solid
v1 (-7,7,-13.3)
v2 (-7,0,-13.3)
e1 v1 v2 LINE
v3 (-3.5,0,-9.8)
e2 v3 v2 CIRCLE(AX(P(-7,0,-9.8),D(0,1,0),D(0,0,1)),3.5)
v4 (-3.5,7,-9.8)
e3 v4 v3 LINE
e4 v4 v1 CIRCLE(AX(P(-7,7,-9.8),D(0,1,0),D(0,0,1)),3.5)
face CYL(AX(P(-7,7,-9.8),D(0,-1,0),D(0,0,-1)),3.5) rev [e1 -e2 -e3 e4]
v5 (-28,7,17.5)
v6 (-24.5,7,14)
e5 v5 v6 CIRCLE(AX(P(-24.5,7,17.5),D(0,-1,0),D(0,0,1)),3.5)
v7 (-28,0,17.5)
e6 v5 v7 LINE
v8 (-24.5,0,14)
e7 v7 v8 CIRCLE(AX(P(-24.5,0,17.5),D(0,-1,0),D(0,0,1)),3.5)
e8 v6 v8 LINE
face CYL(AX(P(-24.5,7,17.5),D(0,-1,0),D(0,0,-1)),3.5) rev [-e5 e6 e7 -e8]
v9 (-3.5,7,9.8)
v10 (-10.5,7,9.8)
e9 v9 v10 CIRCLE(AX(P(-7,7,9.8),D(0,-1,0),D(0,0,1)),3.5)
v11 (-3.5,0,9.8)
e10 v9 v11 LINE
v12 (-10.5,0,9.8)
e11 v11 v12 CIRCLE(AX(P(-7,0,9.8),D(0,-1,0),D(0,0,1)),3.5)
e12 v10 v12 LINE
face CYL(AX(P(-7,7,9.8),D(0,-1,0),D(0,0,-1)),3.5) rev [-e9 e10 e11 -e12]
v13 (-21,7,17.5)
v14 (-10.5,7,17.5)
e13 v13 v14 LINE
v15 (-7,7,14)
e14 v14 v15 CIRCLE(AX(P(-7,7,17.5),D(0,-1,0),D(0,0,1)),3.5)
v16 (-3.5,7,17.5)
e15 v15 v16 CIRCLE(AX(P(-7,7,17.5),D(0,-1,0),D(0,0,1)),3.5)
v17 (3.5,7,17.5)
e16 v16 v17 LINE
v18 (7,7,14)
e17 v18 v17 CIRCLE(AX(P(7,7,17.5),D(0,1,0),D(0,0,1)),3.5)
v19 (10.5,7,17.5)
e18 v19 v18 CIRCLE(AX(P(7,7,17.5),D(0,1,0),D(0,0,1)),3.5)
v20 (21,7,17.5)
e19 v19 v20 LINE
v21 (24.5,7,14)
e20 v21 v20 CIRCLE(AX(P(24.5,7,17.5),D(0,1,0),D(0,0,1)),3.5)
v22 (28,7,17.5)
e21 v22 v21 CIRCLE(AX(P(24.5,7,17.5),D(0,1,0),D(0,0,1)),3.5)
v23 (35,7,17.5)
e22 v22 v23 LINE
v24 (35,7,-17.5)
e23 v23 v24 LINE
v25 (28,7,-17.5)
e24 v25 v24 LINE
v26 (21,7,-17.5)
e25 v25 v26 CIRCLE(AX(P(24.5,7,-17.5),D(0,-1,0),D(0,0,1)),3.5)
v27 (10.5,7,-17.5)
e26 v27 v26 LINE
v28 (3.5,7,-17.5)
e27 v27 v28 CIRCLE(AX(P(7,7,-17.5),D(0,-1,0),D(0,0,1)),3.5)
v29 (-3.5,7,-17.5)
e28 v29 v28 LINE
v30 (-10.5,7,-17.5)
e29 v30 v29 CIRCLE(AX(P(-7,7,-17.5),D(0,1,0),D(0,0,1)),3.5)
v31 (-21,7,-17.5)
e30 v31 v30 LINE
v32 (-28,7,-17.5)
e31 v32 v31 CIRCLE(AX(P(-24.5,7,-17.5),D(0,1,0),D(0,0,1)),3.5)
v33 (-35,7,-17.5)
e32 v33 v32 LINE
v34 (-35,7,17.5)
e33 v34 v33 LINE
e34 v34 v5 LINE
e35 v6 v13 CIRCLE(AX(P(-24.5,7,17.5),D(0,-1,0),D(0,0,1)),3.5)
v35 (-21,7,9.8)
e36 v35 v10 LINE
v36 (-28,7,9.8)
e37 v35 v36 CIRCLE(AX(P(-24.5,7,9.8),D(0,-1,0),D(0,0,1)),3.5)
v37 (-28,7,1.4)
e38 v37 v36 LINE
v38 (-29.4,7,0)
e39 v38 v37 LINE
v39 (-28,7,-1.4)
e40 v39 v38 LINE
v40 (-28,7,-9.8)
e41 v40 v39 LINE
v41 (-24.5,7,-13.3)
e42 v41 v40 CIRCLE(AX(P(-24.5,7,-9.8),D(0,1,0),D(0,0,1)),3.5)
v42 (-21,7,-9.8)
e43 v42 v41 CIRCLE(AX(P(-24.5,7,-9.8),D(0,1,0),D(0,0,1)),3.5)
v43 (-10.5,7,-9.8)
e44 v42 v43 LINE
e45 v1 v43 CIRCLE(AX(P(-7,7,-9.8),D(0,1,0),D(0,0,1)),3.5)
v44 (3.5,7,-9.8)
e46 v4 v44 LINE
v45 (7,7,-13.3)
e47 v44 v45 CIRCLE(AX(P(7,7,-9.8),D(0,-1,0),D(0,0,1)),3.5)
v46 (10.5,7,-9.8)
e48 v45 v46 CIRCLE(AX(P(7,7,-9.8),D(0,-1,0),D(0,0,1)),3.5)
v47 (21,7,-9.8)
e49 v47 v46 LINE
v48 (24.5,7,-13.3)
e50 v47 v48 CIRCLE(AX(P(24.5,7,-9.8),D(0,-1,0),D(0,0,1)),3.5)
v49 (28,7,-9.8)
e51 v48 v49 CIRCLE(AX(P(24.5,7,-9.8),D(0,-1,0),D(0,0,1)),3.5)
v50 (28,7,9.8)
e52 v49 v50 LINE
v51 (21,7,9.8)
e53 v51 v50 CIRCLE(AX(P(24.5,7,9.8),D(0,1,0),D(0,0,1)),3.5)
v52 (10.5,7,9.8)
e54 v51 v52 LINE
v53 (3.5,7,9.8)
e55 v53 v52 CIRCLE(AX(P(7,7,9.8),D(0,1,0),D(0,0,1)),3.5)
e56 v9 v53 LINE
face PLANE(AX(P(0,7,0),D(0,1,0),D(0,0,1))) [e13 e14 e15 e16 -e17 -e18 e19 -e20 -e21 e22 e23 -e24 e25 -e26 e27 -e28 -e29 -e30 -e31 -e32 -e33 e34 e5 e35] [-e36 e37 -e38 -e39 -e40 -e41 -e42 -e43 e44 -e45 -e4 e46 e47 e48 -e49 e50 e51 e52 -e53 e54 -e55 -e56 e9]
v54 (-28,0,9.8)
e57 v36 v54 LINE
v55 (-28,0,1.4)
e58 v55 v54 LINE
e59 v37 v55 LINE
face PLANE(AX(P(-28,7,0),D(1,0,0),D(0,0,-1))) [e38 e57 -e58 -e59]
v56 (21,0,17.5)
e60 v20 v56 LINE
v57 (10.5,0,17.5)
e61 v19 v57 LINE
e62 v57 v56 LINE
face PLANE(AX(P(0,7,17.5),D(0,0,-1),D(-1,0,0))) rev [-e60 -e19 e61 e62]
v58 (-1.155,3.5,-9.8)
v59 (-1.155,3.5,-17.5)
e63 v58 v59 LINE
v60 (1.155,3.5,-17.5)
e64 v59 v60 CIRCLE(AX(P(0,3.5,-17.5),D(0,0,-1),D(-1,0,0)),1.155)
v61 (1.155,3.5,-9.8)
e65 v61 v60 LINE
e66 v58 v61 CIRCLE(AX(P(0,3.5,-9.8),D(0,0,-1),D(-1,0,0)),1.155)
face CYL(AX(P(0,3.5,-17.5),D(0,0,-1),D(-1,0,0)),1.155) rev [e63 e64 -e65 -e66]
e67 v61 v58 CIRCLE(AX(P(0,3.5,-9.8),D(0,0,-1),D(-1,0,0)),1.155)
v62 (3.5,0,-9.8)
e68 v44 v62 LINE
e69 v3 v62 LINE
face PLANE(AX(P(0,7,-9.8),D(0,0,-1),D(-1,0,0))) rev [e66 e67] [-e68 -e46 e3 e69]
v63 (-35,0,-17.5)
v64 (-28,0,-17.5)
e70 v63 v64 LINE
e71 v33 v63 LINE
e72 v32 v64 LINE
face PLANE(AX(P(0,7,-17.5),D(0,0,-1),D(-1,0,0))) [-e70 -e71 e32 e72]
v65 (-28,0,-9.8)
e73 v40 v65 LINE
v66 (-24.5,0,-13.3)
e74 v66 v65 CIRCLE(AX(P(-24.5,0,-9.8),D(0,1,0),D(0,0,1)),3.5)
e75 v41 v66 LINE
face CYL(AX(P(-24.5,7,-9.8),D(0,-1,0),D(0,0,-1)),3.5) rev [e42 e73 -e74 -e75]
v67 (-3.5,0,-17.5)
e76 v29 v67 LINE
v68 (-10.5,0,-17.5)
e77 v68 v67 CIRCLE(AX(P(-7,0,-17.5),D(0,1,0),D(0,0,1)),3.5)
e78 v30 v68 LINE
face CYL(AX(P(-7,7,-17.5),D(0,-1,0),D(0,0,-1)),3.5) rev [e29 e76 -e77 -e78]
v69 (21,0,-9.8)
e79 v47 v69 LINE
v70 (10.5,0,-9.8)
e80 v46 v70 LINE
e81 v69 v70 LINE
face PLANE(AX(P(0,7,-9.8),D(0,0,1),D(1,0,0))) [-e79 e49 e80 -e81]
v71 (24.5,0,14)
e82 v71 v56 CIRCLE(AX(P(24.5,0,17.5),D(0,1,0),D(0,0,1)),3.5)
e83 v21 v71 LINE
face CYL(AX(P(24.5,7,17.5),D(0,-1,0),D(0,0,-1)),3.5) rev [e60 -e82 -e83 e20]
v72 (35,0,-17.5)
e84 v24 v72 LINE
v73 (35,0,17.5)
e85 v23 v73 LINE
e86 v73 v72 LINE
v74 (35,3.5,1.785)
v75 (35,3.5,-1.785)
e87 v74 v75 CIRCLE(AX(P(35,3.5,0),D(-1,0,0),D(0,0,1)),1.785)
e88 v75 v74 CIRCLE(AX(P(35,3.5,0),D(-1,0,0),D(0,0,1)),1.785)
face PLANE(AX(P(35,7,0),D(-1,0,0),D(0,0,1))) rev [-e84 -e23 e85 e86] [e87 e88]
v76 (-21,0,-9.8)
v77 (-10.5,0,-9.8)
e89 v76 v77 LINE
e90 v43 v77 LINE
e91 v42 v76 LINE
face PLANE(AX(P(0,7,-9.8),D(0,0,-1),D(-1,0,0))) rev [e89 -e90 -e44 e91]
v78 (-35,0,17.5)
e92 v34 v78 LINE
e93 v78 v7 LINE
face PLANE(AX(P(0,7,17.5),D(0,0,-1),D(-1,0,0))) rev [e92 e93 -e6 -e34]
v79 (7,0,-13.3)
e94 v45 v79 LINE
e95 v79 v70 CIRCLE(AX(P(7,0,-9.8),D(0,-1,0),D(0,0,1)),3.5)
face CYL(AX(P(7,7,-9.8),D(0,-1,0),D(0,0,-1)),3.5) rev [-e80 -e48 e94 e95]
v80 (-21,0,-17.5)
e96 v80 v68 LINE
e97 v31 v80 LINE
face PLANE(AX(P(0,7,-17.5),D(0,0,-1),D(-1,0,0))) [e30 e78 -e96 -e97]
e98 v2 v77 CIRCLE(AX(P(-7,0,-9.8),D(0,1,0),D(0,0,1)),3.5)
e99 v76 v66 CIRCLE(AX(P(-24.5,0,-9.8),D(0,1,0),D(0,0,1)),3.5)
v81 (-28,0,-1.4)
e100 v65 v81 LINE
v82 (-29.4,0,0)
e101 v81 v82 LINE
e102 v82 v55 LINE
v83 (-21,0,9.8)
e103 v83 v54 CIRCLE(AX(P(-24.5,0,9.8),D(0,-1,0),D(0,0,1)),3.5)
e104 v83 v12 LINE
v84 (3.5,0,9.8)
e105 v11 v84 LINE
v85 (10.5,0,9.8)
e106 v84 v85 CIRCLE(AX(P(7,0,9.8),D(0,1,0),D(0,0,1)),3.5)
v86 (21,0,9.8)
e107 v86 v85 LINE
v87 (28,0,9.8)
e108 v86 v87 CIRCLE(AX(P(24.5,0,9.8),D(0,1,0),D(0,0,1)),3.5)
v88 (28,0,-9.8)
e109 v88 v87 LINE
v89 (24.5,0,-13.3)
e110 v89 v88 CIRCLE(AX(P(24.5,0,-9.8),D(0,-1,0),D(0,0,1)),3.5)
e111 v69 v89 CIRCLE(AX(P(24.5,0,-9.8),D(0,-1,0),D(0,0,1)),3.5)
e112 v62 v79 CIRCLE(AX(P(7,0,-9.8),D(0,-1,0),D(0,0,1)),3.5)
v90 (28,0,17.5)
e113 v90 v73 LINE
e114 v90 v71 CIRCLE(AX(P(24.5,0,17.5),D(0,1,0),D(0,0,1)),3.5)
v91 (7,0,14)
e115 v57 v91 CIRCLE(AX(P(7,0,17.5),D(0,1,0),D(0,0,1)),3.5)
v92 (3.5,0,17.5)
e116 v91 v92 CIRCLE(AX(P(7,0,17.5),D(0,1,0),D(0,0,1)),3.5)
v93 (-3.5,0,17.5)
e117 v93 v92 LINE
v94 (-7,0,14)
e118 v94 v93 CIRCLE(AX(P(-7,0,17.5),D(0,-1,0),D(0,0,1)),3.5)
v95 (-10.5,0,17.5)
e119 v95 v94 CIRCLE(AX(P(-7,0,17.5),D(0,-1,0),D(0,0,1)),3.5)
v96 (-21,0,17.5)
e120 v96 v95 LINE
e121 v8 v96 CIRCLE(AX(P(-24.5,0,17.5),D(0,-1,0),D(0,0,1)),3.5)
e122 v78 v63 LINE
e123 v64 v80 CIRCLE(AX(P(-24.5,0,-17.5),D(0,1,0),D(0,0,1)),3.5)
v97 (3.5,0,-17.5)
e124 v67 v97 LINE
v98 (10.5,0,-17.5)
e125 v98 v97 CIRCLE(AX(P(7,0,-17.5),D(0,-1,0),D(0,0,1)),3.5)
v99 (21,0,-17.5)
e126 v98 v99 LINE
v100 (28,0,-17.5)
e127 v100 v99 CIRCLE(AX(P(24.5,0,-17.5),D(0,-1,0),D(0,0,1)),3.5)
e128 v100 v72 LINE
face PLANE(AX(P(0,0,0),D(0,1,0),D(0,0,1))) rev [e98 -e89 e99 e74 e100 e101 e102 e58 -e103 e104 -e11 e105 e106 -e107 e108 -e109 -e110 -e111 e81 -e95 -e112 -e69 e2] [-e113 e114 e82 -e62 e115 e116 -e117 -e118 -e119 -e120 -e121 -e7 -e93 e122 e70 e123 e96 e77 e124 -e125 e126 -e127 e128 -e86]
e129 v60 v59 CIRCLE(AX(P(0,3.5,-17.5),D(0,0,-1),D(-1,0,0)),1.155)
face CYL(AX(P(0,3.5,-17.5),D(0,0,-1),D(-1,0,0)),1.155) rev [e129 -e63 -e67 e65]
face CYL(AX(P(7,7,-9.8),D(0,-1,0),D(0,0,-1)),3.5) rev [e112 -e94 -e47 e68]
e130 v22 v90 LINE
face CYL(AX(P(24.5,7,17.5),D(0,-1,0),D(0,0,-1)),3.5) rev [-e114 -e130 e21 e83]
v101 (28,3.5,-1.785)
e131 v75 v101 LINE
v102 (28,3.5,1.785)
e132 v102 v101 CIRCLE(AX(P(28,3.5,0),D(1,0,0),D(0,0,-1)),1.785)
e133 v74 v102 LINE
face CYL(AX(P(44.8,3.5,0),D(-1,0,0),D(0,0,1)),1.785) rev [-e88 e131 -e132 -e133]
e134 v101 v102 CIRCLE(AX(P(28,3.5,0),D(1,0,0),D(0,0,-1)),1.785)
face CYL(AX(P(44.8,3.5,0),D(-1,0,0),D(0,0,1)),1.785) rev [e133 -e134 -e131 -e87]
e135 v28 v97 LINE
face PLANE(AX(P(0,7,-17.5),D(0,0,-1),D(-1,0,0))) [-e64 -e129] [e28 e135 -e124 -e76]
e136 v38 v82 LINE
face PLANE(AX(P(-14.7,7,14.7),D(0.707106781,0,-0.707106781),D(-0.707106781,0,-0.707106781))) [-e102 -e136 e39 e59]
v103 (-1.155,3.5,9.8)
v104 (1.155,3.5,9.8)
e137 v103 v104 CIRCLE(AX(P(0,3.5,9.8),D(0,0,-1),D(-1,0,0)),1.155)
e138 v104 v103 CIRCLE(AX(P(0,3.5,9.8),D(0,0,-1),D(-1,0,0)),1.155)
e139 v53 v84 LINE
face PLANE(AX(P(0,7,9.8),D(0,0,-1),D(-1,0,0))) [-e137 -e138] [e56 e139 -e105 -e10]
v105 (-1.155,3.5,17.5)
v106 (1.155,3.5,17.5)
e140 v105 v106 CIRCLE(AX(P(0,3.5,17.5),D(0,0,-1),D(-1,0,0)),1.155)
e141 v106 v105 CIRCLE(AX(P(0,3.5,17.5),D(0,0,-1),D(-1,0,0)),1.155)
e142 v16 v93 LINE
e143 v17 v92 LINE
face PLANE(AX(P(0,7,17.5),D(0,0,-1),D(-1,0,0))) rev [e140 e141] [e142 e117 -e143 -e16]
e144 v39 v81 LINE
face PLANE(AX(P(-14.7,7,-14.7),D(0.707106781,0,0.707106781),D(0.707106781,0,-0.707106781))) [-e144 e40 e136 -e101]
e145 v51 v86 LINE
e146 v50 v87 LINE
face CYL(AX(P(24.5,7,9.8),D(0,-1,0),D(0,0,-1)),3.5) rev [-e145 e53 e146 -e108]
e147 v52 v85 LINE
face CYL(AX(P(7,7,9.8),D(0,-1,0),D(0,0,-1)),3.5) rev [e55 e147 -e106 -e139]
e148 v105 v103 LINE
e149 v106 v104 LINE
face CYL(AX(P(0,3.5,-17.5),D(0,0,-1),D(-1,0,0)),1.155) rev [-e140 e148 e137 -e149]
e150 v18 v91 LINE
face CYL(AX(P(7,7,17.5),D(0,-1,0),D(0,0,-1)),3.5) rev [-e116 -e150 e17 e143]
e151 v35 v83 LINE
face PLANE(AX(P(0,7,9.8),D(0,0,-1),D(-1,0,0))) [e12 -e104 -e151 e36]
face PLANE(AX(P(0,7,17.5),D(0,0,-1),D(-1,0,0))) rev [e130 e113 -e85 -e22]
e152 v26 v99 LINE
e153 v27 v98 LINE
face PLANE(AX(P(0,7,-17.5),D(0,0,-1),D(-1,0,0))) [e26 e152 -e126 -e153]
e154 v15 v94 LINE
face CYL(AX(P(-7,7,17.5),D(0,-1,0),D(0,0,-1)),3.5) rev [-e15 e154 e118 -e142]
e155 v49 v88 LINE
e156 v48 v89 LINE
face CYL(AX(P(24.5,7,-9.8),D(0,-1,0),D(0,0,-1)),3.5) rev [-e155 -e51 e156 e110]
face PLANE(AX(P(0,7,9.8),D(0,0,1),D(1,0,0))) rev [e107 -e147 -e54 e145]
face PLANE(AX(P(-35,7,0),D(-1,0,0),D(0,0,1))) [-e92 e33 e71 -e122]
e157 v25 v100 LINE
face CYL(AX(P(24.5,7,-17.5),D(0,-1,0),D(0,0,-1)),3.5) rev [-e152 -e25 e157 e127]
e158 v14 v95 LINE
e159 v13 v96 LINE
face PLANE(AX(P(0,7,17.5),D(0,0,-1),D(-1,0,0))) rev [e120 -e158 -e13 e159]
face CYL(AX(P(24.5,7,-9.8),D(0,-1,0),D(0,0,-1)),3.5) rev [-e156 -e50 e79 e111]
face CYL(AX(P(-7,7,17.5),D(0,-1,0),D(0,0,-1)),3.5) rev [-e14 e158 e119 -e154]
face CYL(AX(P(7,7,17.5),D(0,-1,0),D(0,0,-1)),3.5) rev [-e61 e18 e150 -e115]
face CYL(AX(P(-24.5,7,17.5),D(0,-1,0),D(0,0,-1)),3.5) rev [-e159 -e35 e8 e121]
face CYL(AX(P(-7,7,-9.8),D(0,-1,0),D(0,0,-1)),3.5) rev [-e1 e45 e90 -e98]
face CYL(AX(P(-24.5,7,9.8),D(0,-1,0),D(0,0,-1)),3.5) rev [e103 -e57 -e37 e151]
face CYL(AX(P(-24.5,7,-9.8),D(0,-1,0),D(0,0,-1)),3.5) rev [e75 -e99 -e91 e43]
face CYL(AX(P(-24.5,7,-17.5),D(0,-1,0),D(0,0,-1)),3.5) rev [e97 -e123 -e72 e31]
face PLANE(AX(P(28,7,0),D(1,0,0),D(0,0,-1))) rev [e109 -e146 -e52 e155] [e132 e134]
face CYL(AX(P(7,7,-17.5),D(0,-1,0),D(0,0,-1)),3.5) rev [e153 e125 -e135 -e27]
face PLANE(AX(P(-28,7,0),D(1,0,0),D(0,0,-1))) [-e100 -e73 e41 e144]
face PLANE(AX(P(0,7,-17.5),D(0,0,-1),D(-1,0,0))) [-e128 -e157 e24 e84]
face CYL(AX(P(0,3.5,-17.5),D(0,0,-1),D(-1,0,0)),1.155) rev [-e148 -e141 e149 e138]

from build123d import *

# Parameters (mm, degrees)
BOSS_EXTRUDE1_DEPTH = 10
M4_TAPPED_HOLE1_D   = 3.3
CUT_EXTRUDE1_START  = -30
SKETCH4_R           = 2.55
CUT_EXTRUDE1_DEPTH  = 84
SCALE_FACTOR1_SCALE = 0.7


with BuildPart() as part:
    # Sketch1 → Boss-Extrude1 (new body)
    with BuildSketch(Plane(origin=(0, 0, 0), x_dir=(1, 0, 0), z_dir=(0, 1, 0))):
        with BuildLine():
            Line((-50, -25), (-40, -25))
            ThreePointArc((-40, -25), (-35, -20), (-30, -25))
            Line((-30, -25), (-15, -25))
            ThreePointArc((-15, -25), (-10, -20), (-5, -25))
            Line((-5, -25), (5, -25))
            ThreePointArc((5, -25), (10, -20), (15, -25))
            Line((15, -25), (30, -25))
            ThreePointArc((30, -25), (35, -20), (40, -25))
            Line((40, -25), (50, -25))
            Line((50, -25), (50, 25))
            Line((50, 25), (40, 25))
            ThreePointArc((40, 25), (35, 20), (30, 25))
            Line((30, 25), (15, 25))
            ThreePointArc((15, 25), (10, 20), (5, 25))
            Line((5, 25), (-5, 25))
            ThreePointArc((-5, 25), (-10, 20), (-15, 25))
            Line((-15, 25), (-30, 25))
            ThreePointArc((-30, 25), (-35, 20), (-40, 25))
            Line((-40, 25), (-50, 25))
            Line((-50, 25), (-50, -25))
        make_face()
        with BuildLine():
            Line((-40, 14), (-40, 2))
            Line((-40, 2), (-42, 0))
            Line((-42, 0), (-40, -2))
            Line((-40, -2), (-40, -14))
            ThreePointArc((-40, -14), (-35, -19), (-30, -14))
            Line((-30, -14), (-15, -14))
            ThreePointArc((-15, -14), (-10, -19), (-5, -14))
            Line((-5, -14), (5, -14))
            ThreePointArc((5, -14), (10, -19), (15, -14))
            Line((15, -14), (30, -14))
            ThreePointArc((30, -14), (35, -19), (40, -14))
            Line((40, -14), (40, 14))
            ThreePointArc((40, 14), (35, 19), (30, 14))
            Line((30, 14), (15, 14))
            ThreePointArc((15, 14), (10, 19), (5, 14))
            Line((5, 14), (0, 14))
            Line((0, 14), (-5, 14))
            ThreePointArc((-5, 14), (-10, 19), (-15, 14))
            Line((-15, 14), (-30, 14))
            ThreePointArc((-30, 14), (-35, 19), (-40, 14))
        make_face(mode=Mode.SUBTRACT)
    extrude(amount=BOSS_EXTRUDE1_DEPTH)

    # M4 Tapped Hole1 (through all)
    with Locations(Plane(origin=(0, 0, -25), x_dir=(-1, 0, 0), z_dir=(0, 0, -1))):
        with Locations((0, 5)):
            Hole(M4_TAPPED_HOLE1_D / 2)

    # Sketch4 → Cut-Extrude1 (cut)
    with BuildSketch(Plane.ZY.offset(50).offset(CUT_EXTRUDE1_START)):
        with Locations((0, 5)):
            Circle(SKETCH4_R)
    extrude(amount=-CUT_EXTRUDE1_DEPTH, mode=Mode.SUBTRACT)


with BuildPart() as part_1:
    # Scale factor1: scaled about (0, 0, 0)
    add(part.part.scale(SCALE_FACTOR1_SCALE))


solid = part_1.part
